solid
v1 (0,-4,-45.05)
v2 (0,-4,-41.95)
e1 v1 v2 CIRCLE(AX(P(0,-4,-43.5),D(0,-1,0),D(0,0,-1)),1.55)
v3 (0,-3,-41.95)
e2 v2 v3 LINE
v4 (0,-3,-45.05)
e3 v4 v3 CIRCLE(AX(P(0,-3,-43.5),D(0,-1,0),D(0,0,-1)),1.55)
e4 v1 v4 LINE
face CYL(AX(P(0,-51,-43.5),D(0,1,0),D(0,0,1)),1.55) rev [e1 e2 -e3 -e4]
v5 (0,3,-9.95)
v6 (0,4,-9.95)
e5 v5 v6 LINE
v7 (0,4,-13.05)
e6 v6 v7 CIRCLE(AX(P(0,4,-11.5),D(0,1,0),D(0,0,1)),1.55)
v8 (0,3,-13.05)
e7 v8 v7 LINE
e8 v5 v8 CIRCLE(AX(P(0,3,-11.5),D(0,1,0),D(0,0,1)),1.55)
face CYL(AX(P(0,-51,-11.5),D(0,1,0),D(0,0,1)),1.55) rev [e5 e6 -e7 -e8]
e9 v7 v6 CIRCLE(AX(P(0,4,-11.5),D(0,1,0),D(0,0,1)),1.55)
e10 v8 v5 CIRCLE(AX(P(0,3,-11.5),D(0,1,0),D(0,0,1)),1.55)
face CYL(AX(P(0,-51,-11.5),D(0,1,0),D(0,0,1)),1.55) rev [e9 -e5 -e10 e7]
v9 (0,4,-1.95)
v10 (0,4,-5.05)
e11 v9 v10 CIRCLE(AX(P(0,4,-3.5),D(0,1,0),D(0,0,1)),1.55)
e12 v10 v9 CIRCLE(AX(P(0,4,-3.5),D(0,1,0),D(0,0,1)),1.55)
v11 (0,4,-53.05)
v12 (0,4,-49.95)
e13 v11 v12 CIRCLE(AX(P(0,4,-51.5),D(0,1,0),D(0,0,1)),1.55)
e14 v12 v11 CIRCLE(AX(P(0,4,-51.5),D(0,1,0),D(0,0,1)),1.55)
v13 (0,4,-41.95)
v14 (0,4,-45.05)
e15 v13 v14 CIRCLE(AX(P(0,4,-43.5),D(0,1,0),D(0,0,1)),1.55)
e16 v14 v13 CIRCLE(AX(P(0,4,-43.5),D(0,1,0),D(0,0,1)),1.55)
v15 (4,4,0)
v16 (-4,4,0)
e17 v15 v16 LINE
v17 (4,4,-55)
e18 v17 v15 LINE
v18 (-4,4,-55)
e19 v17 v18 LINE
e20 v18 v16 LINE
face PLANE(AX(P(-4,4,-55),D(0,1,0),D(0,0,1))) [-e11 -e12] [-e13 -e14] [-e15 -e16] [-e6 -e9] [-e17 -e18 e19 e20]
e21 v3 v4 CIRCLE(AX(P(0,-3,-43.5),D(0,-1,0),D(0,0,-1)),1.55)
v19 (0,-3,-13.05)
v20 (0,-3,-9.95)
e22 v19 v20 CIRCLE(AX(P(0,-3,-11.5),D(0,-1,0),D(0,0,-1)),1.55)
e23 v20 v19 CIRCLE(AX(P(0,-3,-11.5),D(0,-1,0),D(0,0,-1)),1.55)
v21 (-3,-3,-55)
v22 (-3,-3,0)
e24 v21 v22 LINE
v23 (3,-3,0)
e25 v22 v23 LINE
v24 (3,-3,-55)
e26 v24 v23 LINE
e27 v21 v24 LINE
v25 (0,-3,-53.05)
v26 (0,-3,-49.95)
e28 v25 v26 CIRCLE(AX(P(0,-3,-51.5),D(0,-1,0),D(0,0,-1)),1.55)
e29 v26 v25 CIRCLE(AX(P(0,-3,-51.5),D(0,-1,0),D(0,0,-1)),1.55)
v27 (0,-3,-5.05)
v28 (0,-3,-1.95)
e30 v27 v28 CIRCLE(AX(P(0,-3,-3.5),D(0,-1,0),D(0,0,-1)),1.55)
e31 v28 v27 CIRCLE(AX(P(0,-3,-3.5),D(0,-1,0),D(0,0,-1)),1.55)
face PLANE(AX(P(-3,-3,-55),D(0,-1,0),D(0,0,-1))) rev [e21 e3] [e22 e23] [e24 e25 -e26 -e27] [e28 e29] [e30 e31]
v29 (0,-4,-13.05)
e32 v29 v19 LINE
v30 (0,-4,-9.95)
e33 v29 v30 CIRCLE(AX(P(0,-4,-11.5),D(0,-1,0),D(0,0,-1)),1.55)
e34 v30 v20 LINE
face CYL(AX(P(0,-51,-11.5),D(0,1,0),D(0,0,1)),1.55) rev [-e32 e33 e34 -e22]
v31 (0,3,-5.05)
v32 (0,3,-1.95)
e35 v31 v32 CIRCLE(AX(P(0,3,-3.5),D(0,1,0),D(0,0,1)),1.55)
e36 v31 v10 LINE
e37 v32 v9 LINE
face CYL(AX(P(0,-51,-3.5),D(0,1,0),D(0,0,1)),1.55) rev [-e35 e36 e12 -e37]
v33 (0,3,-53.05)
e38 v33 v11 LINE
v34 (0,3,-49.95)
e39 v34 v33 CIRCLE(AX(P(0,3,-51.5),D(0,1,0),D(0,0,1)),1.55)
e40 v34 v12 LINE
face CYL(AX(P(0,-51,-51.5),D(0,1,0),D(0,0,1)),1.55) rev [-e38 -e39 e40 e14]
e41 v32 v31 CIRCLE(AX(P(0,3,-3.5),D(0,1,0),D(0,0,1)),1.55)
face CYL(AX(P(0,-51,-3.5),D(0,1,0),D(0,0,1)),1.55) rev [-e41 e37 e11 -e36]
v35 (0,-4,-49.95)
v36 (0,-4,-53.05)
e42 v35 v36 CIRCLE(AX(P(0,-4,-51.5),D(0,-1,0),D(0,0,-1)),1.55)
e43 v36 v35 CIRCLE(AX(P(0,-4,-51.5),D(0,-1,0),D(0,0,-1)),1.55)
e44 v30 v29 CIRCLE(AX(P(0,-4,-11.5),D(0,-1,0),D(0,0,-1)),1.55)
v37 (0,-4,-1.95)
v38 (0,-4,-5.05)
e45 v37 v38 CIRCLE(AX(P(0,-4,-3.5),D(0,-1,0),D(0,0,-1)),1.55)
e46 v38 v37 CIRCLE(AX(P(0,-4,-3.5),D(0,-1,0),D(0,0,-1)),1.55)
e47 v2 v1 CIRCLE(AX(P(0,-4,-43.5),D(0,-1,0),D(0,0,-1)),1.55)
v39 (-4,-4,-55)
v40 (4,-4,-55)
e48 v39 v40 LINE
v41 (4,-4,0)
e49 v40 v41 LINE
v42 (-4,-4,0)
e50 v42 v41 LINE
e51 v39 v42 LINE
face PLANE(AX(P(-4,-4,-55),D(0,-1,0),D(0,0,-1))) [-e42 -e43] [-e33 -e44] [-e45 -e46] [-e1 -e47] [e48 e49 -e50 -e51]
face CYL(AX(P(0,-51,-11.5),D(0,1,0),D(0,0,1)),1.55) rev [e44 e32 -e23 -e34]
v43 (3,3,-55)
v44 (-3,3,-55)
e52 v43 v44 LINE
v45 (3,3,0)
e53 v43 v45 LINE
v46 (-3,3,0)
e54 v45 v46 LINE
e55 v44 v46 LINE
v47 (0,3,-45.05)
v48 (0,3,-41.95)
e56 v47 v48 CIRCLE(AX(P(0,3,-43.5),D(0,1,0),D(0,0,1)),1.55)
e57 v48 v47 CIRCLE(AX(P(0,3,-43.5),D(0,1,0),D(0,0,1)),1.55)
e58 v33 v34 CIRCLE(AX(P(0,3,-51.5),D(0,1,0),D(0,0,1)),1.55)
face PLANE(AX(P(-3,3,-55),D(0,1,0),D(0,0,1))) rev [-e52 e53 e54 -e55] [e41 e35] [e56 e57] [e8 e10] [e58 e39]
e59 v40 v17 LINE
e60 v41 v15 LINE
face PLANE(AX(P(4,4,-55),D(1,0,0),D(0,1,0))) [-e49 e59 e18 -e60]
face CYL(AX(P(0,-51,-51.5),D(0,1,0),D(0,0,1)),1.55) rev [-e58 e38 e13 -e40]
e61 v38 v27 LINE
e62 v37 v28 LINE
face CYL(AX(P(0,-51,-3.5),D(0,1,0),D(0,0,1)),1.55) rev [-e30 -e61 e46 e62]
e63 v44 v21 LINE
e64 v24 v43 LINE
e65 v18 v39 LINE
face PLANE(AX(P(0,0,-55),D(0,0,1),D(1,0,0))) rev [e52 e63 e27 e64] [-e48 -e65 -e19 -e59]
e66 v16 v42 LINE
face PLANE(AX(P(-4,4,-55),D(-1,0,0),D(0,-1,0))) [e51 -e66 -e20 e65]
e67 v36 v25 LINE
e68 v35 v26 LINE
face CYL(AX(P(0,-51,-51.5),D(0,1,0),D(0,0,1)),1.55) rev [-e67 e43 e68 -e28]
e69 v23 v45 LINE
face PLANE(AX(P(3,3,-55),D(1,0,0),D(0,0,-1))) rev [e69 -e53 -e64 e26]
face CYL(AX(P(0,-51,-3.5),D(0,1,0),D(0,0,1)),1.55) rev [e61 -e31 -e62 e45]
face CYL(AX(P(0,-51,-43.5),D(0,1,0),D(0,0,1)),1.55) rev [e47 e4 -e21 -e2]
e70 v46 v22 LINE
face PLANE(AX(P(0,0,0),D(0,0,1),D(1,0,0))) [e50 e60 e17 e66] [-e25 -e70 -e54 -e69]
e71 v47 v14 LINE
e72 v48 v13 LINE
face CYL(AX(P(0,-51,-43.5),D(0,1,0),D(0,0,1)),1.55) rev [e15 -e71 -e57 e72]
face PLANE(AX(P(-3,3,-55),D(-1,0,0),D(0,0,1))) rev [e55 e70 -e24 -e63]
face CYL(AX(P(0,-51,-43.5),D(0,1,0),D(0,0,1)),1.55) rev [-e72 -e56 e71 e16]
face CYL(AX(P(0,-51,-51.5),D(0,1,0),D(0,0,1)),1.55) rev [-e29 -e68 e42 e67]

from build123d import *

# Parameters (mm, degrees)
SKETCH_1_W          = 8
SKETCH_1_H          = 8
SKETCH_1_W_2        = 6
SKETCH_1_H_2        = 6
EXTRUDE_1_DEPTH     = 55
SKETCH_3_R          = 1.55
CUT_EXTRUDE_1_DEPTH = 55


with BuildPart() as part:
    # 草图1 → 凸台-拉伸1 (new body)
    with BuildSketch(Plane.XY):
        Rectangle(SKETCH_1_W, SKETCH_1_H)
        Rectangle(SKETCH_1_W_2, SKETCH_1_H_2, mode=Mode.SUBTRACT)
    extrude(amount=-EXTRUDE_1_DEPTH)

    # 草图3 → 切除-拉伸1 (cut)
    with BuildSketch(Plane(origin=(0, 4, 0), x_dir=(1, 0, 0), z_dir=(0, 1, 0))):
        with Locations(Location((0, 3.5, 0), (0, 0, 90))):
            Circle(SKETCH_3_R)
        with Locations(Location((0, 11.5, 0), (0, 0, 90))):
            Circle(SKETCH_3_R)
        with Locations(Location((0, 43.5, 0), (0, 0, 90))):
            Circle(SKETCH_3_R)
        with Locations(Location((0, 51.5, 0), (0, 0, 90))):
            Circle(SKETCH_3_R)
    extrude(amount=-CUT_EXTRUDE_1_DEPTH, mode=Mode.SUBTRACT)


solid = part.part
